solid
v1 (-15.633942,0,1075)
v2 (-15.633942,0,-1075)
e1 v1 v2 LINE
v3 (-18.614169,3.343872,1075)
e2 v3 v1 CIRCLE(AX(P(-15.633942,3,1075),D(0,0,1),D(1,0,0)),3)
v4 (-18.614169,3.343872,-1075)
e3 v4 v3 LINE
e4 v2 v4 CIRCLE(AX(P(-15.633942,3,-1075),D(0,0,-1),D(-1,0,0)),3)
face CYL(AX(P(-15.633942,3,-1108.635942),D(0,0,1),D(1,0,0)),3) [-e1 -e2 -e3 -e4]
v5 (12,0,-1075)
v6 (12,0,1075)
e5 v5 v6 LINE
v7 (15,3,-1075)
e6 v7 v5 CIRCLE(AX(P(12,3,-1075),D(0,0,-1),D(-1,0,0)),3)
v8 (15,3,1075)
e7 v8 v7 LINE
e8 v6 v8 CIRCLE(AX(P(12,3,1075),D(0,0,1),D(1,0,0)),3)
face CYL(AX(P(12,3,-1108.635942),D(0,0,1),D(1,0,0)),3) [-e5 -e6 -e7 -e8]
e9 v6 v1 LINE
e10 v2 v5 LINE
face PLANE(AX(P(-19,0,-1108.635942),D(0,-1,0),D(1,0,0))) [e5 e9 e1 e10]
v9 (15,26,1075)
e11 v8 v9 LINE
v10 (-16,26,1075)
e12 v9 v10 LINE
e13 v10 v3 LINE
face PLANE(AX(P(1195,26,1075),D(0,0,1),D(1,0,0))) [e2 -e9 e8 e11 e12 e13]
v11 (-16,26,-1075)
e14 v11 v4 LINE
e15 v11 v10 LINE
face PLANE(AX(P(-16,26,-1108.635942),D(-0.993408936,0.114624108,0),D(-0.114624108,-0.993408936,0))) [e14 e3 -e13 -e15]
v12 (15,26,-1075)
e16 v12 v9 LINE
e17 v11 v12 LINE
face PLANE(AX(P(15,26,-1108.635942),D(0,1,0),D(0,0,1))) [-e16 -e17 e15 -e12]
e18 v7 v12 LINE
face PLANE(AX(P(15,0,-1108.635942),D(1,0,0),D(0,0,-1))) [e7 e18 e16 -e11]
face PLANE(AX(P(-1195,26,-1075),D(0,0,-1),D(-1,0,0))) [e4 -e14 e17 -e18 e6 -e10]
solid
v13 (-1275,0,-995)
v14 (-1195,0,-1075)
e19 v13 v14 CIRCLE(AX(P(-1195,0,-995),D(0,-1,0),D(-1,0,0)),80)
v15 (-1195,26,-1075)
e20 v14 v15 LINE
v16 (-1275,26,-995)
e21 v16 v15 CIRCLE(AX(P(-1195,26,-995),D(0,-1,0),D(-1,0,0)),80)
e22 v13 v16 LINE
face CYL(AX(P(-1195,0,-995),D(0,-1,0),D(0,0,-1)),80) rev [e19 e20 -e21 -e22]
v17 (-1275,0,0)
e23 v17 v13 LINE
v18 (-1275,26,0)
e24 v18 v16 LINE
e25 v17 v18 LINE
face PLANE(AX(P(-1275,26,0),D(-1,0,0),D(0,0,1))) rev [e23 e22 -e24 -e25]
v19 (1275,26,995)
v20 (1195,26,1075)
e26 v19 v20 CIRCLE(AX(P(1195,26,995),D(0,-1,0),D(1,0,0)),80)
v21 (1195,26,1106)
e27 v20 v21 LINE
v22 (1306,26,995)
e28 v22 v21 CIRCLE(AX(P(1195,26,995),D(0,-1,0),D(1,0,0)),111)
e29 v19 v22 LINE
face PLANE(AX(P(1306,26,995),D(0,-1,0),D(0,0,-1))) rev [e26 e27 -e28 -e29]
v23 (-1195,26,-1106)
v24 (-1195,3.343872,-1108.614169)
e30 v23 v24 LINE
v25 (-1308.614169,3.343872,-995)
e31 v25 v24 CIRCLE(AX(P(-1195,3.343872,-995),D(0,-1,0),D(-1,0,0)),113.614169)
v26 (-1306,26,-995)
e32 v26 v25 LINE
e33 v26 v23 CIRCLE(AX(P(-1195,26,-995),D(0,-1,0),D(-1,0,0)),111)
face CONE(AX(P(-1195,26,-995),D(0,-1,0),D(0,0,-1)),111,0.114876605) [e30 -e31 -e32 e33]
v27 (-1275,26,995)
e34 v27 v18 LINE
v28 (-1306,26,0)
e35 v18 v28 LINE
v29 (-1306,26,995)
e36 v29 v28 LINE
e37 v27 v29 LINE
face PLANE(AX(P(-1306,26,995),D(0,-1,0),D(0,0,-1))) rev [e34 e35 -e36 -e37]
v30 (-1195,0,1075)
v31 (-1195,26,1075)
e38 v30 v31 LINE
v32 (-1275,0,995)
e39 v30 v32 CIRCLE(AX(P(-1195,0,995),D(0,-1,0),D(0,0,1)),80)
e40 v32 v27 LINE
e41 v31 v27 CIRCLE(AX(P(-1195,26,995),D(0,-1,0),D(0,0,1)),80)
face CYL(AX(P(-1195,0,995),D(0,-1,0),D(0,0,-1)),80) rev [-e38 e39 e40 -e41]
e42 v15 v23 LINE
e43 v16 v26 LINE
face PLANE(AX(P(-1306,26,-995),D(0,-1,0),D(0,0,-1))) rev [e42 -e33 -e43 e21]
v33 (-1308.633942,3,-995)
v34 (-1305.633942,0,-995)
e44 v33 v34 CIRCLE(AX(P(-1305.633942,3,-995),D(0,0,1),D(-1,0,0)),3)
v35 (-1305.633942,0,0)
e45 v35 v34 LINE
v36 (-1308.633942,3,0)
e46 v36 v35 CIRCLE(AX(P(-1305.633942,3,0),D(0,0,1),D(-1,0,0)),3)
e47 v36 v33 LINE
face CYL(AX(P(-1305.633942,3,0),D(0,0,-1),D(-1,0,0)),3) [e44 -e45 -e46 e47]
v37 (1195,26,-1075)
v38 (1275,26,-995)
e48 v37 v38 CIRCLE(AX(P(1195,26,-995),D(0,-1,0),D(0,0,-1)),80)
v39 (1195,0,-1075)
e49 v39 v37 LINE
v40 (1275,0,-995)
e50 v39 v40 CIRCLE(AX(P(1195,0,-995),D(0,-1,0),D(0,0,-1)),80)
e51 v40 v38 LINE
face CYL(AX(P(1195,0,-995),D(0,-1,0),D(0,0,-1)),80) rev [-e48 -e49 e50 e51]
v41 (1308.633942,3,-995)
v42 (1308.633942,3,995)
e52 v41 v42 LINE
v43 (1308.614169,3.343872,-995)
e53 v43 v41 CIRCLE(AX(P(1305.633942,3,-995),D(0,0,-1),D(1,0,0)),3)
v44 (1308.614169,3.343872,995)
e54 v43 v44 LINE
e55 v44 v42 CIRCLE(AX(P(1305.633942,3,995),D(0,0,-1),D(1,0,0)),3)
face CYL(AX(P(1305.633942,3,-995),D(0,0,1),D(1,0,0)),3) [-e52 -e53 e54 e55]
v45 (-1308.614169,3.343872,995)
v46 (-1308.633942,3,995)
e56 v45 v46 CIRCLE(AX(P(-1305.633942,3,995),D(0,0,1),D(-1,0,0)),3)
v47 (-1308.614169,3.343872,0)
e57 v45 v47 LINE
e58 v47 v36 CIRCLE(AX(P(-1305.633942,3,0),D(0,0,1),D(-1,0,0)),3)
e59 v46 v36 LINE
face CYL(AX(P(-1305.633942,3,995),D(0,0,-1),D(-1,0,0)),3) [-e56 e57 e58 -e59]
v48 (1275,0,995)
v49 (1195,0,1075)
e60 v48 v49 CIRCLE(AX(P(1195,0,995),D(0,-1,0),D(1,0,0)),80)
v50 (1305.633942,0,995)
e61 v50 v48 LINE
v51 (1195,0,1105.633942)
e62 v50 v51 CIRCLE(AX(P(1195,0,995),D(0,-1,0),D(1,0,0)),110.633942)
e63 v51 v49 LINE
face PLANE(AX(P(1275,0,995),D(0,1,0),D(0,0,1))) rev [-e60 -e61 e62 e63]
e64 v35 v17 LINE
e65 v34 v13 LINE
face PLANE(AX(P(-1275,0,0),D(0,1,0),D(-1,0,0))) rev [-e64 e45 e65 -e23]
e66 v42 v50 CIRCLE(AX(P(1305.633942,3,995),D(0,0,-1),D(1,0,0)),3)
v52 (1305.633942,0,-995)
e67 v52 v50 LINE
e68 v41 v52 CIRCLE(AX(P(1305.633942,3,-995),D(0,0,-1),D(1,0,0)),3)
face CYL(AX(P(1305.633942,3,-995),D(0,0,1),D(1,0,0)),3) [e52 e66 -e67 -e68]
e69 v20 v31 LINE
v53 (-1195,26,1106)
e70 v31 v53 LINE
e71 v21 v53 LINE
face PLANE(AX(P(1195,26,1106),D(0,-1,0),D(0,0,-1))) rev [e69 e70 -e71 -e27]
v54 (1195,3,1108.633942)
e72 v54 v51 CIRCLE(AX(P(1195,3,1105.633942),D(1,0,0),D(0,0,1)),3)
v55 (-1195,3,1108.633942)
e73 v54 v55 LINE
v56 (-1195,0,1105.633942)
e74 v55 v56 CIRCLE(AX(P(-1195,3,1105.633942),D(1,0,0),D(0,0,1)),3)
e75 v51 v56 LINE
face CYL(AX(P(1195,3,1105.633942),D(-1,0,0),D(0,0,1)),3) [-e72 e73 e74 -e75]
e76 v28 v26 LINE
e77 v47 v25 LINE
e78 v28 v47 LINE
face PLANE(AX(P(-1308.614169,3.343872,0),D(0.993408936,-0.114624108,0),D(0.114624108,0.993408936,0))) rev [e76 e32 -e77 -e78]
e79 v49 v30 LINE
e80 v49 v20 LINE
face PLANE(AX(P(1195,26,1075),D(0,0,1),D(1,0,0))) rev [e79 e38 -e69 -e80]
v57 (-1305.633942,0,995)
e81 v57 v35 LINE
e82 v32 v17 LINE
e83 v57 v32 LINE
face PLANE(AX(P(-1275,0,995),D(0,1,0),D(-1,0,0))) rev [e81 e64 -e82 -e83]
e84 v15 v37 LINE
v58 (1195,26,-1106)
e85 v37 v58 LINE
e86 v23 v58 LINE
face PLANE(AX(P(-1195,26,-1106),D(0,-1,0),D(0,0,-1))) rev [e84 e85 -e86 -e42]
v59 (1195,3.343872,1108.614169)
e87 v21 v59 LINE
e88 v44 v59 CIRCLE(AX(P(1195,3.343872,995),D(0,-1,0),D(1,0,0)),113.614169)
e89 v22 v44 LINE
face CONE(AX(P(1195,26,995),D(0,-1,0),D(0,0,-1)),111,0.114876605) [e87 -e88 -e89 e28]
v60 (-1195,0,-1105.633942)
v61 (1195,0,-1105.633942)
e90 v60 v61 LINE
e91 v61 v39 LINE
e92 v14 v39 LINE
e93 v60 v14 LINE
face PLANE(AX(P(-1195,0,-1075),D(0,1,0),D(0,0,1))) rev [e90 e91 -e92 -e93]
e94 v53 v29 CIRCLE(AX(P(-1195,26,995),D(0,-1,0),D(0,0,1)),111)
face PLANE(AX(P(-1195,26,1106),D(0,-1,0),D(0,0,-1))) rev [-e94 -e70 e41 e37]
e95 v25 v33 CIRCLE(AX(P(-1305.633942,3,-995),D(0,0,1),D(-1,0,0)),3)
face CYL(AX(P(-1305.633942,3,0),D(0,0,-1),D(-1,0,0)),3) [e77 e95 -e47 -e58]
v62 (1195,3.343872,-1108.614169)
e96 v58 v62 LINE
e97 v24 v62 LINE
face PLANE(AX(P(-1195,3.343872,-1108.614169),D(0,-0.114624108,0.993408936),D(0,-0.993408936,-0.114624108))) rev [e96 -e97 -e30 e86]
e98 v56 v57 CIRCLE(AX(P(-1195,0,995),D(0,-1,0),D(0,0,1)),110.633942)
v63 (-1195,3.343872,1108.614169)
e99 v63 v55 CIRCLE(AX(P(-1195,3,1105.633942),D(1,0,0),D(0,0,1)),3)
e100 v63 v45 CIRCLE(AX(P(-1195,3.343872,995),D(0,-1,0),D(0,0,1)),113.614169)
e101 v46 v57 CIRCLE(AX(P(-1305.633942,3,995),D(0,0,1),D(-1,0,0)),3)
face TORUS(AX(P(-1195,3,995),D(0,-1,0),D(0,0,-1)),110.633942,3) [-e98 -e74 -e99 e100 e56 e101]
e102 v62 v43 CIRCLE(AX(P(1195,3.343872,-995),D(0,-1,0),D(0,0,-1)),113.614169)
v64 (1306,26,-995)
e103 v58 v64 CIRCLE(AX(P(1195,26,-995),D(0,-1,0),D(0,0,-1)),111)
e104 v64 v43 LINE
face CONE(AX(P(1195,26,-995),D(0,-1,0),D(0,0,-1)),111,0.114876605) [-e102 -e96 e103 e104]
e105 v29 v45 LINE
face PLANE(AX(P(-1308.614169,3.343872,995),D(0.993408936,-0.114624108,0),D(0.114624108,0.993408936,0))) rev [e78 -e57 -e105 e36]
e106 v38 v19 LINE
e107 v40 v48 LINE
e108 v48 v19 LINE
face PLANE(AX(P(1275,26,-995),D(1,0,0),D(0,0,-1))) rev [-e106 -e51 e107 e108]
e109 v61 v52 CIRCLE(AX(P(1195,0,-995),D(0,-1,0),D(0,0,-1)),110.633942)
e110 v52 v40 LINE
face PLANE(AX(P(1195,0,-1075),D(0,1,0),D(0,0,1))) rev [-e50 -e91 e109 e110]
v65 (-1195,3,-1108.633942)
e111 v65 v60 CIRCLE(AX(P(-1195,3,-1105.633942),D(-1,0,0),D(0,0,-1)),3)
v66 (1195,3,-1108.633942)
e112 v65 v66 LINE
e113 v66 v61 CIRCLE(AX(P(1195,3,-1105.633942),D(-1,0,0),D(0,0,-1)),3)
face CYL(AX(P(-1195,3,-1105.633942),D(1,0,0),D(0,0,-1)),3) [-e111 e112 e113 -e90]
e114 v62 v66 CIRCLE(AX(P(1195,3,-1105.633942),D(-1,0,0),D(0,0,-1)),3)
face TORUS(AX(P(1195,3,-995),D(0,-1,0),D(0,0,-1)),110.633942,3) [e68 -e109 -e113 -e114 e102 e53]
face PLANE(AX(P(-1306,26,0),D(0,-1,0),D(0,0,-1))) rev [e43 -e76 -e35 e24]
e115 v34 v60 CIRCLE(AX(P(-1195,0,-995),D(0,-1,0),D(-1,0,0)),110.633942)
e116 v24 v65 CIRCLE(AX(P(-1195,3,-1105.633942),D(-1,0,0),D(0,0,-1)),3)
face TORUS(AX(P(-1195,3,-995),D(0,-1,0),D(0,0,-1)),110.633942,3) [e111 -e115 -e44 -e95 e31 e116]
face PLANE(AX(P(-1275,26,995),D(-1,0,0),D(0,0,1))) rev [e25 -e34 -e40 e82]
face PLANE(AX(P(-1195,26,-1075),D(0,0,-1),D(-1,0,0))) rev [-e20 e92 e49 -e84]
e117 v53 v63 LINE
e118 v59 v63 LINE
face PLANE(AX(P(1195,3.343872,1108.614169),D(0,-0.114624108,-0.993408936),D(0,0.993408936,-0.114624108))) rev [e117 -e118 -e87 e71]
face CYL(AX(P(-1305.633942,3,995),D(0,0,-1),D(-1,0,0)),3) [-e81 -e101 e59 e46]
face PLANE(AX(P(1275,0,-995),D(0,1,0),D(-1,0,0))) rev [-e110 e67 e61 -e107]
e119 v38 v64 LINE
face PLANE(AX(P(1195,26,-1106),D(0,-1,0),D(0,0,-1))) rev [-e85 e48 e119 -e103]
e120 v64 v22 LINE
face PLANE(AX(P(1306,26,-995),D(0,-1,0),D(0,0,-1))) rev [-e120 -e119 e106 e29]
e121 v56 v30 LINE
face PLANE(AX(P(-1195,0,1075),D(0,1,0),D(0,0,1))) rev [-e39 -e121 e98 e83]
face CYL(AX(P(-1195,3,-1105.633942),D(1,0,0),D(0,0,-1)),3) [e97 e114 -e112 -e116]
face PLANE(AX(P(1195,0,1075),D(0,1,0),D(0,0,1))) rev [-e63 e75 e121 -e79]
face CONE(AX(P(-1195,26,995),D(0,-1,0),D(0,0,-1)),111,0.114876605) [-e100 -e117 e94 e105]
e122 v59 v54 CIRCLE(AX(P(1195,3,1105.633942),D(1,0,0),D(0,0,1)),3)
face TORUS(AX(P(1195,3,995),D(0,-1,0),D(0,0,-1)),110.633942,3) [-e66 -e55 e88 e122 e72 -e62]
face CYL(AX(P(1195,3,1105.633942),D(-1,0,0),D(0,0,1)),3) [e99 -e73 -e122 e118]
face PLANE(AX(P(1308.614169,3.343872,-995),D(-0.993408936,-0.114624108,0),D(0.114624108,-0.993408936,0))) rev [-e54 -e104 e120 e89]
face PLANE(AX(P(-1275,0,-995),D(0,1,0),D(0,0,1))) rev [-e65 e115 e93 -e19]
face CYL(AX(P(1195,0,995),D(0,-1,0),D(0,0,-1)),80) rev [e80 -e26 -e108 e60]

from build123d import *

# Parameters (mm, degrees)
EXTRUDE_1_REACH             = 1717.304
EXTRUDE_1_DIRECTION_2_REACH = 1717.304
FILLET_1_R                  = 3


with BuildPart() as part:
    # 扫描1: sweep along a path in 草图1
    with BuildLine(Plane(origin=(0, 0, 0), x_dir=(1, 0, 0), z_dir=(0, 1, 0))) as sweep_1_path:
        Line((-1195, -1090), (1195, -1090))
        ThreePointArc((1195, -1090), (1262.175144213, -1062.175144213), (1290, -995))
        Line((1290, -995), (1290, 995))
        ThreePointArc((1290, 995), (1262.175144213, 1062.175144213), (1195, 1090))
        Line((1195, 1090), (-1195, 1090))
        ThreePointArc((-1195, 1090), (-1262.175144213, 1062.175144213), (-1290, 995))
        Line((-1290, 995), (-1290, -995))
        ThreePointArc((-1290, -995), (-1262.175144213, -1062.175144213), (-1195, -1090))
    # 草图2 → 扫描1 (sweep)
    with BuildSketch(Plane.XY):
        with BuildLine():
            Line((-1275, 0), (-1305.63394177, 0))
            ThreePointArc((-1305.63394177, 0), (-1307.873541843, 1.003956034), (-1308.614168578, 3.343872324))
            Line((-1308.614168578, 3.343872324), (-1306, 26))
            Line((-1306, 26), (-1275, 26))
            Line((-1275, 26), (-1275, 0))
        make_face()
    sweep(path=sweep_1_path.line)


with BuildPart() as body_2:

    # 草图3 → 凸台-拉伸1 (new, up to next)
    with BuildSketch(Plane.XY, mode=Mode.PRIVATE) as extrude_1_sk1:
        Polygon((-16, 26), (-19, 0), (15, 0), (15, 26), align=None)
    extrude_1_tool1 = extrude(extrude_1_sk1.sketch, amount=EXTRUDE_1_REACH, mode=Mode.PRIVATE) - part.part
    add(extrude_1_tool1.solids().sort_by_distance((-1.261538, 12.8, 0))[0])


    # 草图3 → 凸台-拉伸1 direction 2 (add, up to next)
    with BuildSketch(Plane.XY, mode=Mode.PRIVATE) as extrude_1_direction_2_sk1:
        Polygon((-16, 26), (-19, 0), (15, 0), (15, 26), align=None)
    extrude_1_direction_2_tool1 = extrude(extrude_1_direction_2_sk1.sketch, amount=-EXTRUDE_1_DIRECTION_2_REACH, mode=Mode.PRIVATE) - part.part
    add(extrude_1_direction_2_tool1.solids().sort_by_distance((-1.261538, 12.8, 0))[0])

    # 圆角1
    fillet_1_edges = [body_2.edges().sort_by_distance(p)[0] for p in [
        (15, 0, 0),
        (-19, 0, 0),
    ]]
    fillet(fillet_1_edges, radius=FILLET_1_R)


solid = Compound([part.part, body_2.part])
